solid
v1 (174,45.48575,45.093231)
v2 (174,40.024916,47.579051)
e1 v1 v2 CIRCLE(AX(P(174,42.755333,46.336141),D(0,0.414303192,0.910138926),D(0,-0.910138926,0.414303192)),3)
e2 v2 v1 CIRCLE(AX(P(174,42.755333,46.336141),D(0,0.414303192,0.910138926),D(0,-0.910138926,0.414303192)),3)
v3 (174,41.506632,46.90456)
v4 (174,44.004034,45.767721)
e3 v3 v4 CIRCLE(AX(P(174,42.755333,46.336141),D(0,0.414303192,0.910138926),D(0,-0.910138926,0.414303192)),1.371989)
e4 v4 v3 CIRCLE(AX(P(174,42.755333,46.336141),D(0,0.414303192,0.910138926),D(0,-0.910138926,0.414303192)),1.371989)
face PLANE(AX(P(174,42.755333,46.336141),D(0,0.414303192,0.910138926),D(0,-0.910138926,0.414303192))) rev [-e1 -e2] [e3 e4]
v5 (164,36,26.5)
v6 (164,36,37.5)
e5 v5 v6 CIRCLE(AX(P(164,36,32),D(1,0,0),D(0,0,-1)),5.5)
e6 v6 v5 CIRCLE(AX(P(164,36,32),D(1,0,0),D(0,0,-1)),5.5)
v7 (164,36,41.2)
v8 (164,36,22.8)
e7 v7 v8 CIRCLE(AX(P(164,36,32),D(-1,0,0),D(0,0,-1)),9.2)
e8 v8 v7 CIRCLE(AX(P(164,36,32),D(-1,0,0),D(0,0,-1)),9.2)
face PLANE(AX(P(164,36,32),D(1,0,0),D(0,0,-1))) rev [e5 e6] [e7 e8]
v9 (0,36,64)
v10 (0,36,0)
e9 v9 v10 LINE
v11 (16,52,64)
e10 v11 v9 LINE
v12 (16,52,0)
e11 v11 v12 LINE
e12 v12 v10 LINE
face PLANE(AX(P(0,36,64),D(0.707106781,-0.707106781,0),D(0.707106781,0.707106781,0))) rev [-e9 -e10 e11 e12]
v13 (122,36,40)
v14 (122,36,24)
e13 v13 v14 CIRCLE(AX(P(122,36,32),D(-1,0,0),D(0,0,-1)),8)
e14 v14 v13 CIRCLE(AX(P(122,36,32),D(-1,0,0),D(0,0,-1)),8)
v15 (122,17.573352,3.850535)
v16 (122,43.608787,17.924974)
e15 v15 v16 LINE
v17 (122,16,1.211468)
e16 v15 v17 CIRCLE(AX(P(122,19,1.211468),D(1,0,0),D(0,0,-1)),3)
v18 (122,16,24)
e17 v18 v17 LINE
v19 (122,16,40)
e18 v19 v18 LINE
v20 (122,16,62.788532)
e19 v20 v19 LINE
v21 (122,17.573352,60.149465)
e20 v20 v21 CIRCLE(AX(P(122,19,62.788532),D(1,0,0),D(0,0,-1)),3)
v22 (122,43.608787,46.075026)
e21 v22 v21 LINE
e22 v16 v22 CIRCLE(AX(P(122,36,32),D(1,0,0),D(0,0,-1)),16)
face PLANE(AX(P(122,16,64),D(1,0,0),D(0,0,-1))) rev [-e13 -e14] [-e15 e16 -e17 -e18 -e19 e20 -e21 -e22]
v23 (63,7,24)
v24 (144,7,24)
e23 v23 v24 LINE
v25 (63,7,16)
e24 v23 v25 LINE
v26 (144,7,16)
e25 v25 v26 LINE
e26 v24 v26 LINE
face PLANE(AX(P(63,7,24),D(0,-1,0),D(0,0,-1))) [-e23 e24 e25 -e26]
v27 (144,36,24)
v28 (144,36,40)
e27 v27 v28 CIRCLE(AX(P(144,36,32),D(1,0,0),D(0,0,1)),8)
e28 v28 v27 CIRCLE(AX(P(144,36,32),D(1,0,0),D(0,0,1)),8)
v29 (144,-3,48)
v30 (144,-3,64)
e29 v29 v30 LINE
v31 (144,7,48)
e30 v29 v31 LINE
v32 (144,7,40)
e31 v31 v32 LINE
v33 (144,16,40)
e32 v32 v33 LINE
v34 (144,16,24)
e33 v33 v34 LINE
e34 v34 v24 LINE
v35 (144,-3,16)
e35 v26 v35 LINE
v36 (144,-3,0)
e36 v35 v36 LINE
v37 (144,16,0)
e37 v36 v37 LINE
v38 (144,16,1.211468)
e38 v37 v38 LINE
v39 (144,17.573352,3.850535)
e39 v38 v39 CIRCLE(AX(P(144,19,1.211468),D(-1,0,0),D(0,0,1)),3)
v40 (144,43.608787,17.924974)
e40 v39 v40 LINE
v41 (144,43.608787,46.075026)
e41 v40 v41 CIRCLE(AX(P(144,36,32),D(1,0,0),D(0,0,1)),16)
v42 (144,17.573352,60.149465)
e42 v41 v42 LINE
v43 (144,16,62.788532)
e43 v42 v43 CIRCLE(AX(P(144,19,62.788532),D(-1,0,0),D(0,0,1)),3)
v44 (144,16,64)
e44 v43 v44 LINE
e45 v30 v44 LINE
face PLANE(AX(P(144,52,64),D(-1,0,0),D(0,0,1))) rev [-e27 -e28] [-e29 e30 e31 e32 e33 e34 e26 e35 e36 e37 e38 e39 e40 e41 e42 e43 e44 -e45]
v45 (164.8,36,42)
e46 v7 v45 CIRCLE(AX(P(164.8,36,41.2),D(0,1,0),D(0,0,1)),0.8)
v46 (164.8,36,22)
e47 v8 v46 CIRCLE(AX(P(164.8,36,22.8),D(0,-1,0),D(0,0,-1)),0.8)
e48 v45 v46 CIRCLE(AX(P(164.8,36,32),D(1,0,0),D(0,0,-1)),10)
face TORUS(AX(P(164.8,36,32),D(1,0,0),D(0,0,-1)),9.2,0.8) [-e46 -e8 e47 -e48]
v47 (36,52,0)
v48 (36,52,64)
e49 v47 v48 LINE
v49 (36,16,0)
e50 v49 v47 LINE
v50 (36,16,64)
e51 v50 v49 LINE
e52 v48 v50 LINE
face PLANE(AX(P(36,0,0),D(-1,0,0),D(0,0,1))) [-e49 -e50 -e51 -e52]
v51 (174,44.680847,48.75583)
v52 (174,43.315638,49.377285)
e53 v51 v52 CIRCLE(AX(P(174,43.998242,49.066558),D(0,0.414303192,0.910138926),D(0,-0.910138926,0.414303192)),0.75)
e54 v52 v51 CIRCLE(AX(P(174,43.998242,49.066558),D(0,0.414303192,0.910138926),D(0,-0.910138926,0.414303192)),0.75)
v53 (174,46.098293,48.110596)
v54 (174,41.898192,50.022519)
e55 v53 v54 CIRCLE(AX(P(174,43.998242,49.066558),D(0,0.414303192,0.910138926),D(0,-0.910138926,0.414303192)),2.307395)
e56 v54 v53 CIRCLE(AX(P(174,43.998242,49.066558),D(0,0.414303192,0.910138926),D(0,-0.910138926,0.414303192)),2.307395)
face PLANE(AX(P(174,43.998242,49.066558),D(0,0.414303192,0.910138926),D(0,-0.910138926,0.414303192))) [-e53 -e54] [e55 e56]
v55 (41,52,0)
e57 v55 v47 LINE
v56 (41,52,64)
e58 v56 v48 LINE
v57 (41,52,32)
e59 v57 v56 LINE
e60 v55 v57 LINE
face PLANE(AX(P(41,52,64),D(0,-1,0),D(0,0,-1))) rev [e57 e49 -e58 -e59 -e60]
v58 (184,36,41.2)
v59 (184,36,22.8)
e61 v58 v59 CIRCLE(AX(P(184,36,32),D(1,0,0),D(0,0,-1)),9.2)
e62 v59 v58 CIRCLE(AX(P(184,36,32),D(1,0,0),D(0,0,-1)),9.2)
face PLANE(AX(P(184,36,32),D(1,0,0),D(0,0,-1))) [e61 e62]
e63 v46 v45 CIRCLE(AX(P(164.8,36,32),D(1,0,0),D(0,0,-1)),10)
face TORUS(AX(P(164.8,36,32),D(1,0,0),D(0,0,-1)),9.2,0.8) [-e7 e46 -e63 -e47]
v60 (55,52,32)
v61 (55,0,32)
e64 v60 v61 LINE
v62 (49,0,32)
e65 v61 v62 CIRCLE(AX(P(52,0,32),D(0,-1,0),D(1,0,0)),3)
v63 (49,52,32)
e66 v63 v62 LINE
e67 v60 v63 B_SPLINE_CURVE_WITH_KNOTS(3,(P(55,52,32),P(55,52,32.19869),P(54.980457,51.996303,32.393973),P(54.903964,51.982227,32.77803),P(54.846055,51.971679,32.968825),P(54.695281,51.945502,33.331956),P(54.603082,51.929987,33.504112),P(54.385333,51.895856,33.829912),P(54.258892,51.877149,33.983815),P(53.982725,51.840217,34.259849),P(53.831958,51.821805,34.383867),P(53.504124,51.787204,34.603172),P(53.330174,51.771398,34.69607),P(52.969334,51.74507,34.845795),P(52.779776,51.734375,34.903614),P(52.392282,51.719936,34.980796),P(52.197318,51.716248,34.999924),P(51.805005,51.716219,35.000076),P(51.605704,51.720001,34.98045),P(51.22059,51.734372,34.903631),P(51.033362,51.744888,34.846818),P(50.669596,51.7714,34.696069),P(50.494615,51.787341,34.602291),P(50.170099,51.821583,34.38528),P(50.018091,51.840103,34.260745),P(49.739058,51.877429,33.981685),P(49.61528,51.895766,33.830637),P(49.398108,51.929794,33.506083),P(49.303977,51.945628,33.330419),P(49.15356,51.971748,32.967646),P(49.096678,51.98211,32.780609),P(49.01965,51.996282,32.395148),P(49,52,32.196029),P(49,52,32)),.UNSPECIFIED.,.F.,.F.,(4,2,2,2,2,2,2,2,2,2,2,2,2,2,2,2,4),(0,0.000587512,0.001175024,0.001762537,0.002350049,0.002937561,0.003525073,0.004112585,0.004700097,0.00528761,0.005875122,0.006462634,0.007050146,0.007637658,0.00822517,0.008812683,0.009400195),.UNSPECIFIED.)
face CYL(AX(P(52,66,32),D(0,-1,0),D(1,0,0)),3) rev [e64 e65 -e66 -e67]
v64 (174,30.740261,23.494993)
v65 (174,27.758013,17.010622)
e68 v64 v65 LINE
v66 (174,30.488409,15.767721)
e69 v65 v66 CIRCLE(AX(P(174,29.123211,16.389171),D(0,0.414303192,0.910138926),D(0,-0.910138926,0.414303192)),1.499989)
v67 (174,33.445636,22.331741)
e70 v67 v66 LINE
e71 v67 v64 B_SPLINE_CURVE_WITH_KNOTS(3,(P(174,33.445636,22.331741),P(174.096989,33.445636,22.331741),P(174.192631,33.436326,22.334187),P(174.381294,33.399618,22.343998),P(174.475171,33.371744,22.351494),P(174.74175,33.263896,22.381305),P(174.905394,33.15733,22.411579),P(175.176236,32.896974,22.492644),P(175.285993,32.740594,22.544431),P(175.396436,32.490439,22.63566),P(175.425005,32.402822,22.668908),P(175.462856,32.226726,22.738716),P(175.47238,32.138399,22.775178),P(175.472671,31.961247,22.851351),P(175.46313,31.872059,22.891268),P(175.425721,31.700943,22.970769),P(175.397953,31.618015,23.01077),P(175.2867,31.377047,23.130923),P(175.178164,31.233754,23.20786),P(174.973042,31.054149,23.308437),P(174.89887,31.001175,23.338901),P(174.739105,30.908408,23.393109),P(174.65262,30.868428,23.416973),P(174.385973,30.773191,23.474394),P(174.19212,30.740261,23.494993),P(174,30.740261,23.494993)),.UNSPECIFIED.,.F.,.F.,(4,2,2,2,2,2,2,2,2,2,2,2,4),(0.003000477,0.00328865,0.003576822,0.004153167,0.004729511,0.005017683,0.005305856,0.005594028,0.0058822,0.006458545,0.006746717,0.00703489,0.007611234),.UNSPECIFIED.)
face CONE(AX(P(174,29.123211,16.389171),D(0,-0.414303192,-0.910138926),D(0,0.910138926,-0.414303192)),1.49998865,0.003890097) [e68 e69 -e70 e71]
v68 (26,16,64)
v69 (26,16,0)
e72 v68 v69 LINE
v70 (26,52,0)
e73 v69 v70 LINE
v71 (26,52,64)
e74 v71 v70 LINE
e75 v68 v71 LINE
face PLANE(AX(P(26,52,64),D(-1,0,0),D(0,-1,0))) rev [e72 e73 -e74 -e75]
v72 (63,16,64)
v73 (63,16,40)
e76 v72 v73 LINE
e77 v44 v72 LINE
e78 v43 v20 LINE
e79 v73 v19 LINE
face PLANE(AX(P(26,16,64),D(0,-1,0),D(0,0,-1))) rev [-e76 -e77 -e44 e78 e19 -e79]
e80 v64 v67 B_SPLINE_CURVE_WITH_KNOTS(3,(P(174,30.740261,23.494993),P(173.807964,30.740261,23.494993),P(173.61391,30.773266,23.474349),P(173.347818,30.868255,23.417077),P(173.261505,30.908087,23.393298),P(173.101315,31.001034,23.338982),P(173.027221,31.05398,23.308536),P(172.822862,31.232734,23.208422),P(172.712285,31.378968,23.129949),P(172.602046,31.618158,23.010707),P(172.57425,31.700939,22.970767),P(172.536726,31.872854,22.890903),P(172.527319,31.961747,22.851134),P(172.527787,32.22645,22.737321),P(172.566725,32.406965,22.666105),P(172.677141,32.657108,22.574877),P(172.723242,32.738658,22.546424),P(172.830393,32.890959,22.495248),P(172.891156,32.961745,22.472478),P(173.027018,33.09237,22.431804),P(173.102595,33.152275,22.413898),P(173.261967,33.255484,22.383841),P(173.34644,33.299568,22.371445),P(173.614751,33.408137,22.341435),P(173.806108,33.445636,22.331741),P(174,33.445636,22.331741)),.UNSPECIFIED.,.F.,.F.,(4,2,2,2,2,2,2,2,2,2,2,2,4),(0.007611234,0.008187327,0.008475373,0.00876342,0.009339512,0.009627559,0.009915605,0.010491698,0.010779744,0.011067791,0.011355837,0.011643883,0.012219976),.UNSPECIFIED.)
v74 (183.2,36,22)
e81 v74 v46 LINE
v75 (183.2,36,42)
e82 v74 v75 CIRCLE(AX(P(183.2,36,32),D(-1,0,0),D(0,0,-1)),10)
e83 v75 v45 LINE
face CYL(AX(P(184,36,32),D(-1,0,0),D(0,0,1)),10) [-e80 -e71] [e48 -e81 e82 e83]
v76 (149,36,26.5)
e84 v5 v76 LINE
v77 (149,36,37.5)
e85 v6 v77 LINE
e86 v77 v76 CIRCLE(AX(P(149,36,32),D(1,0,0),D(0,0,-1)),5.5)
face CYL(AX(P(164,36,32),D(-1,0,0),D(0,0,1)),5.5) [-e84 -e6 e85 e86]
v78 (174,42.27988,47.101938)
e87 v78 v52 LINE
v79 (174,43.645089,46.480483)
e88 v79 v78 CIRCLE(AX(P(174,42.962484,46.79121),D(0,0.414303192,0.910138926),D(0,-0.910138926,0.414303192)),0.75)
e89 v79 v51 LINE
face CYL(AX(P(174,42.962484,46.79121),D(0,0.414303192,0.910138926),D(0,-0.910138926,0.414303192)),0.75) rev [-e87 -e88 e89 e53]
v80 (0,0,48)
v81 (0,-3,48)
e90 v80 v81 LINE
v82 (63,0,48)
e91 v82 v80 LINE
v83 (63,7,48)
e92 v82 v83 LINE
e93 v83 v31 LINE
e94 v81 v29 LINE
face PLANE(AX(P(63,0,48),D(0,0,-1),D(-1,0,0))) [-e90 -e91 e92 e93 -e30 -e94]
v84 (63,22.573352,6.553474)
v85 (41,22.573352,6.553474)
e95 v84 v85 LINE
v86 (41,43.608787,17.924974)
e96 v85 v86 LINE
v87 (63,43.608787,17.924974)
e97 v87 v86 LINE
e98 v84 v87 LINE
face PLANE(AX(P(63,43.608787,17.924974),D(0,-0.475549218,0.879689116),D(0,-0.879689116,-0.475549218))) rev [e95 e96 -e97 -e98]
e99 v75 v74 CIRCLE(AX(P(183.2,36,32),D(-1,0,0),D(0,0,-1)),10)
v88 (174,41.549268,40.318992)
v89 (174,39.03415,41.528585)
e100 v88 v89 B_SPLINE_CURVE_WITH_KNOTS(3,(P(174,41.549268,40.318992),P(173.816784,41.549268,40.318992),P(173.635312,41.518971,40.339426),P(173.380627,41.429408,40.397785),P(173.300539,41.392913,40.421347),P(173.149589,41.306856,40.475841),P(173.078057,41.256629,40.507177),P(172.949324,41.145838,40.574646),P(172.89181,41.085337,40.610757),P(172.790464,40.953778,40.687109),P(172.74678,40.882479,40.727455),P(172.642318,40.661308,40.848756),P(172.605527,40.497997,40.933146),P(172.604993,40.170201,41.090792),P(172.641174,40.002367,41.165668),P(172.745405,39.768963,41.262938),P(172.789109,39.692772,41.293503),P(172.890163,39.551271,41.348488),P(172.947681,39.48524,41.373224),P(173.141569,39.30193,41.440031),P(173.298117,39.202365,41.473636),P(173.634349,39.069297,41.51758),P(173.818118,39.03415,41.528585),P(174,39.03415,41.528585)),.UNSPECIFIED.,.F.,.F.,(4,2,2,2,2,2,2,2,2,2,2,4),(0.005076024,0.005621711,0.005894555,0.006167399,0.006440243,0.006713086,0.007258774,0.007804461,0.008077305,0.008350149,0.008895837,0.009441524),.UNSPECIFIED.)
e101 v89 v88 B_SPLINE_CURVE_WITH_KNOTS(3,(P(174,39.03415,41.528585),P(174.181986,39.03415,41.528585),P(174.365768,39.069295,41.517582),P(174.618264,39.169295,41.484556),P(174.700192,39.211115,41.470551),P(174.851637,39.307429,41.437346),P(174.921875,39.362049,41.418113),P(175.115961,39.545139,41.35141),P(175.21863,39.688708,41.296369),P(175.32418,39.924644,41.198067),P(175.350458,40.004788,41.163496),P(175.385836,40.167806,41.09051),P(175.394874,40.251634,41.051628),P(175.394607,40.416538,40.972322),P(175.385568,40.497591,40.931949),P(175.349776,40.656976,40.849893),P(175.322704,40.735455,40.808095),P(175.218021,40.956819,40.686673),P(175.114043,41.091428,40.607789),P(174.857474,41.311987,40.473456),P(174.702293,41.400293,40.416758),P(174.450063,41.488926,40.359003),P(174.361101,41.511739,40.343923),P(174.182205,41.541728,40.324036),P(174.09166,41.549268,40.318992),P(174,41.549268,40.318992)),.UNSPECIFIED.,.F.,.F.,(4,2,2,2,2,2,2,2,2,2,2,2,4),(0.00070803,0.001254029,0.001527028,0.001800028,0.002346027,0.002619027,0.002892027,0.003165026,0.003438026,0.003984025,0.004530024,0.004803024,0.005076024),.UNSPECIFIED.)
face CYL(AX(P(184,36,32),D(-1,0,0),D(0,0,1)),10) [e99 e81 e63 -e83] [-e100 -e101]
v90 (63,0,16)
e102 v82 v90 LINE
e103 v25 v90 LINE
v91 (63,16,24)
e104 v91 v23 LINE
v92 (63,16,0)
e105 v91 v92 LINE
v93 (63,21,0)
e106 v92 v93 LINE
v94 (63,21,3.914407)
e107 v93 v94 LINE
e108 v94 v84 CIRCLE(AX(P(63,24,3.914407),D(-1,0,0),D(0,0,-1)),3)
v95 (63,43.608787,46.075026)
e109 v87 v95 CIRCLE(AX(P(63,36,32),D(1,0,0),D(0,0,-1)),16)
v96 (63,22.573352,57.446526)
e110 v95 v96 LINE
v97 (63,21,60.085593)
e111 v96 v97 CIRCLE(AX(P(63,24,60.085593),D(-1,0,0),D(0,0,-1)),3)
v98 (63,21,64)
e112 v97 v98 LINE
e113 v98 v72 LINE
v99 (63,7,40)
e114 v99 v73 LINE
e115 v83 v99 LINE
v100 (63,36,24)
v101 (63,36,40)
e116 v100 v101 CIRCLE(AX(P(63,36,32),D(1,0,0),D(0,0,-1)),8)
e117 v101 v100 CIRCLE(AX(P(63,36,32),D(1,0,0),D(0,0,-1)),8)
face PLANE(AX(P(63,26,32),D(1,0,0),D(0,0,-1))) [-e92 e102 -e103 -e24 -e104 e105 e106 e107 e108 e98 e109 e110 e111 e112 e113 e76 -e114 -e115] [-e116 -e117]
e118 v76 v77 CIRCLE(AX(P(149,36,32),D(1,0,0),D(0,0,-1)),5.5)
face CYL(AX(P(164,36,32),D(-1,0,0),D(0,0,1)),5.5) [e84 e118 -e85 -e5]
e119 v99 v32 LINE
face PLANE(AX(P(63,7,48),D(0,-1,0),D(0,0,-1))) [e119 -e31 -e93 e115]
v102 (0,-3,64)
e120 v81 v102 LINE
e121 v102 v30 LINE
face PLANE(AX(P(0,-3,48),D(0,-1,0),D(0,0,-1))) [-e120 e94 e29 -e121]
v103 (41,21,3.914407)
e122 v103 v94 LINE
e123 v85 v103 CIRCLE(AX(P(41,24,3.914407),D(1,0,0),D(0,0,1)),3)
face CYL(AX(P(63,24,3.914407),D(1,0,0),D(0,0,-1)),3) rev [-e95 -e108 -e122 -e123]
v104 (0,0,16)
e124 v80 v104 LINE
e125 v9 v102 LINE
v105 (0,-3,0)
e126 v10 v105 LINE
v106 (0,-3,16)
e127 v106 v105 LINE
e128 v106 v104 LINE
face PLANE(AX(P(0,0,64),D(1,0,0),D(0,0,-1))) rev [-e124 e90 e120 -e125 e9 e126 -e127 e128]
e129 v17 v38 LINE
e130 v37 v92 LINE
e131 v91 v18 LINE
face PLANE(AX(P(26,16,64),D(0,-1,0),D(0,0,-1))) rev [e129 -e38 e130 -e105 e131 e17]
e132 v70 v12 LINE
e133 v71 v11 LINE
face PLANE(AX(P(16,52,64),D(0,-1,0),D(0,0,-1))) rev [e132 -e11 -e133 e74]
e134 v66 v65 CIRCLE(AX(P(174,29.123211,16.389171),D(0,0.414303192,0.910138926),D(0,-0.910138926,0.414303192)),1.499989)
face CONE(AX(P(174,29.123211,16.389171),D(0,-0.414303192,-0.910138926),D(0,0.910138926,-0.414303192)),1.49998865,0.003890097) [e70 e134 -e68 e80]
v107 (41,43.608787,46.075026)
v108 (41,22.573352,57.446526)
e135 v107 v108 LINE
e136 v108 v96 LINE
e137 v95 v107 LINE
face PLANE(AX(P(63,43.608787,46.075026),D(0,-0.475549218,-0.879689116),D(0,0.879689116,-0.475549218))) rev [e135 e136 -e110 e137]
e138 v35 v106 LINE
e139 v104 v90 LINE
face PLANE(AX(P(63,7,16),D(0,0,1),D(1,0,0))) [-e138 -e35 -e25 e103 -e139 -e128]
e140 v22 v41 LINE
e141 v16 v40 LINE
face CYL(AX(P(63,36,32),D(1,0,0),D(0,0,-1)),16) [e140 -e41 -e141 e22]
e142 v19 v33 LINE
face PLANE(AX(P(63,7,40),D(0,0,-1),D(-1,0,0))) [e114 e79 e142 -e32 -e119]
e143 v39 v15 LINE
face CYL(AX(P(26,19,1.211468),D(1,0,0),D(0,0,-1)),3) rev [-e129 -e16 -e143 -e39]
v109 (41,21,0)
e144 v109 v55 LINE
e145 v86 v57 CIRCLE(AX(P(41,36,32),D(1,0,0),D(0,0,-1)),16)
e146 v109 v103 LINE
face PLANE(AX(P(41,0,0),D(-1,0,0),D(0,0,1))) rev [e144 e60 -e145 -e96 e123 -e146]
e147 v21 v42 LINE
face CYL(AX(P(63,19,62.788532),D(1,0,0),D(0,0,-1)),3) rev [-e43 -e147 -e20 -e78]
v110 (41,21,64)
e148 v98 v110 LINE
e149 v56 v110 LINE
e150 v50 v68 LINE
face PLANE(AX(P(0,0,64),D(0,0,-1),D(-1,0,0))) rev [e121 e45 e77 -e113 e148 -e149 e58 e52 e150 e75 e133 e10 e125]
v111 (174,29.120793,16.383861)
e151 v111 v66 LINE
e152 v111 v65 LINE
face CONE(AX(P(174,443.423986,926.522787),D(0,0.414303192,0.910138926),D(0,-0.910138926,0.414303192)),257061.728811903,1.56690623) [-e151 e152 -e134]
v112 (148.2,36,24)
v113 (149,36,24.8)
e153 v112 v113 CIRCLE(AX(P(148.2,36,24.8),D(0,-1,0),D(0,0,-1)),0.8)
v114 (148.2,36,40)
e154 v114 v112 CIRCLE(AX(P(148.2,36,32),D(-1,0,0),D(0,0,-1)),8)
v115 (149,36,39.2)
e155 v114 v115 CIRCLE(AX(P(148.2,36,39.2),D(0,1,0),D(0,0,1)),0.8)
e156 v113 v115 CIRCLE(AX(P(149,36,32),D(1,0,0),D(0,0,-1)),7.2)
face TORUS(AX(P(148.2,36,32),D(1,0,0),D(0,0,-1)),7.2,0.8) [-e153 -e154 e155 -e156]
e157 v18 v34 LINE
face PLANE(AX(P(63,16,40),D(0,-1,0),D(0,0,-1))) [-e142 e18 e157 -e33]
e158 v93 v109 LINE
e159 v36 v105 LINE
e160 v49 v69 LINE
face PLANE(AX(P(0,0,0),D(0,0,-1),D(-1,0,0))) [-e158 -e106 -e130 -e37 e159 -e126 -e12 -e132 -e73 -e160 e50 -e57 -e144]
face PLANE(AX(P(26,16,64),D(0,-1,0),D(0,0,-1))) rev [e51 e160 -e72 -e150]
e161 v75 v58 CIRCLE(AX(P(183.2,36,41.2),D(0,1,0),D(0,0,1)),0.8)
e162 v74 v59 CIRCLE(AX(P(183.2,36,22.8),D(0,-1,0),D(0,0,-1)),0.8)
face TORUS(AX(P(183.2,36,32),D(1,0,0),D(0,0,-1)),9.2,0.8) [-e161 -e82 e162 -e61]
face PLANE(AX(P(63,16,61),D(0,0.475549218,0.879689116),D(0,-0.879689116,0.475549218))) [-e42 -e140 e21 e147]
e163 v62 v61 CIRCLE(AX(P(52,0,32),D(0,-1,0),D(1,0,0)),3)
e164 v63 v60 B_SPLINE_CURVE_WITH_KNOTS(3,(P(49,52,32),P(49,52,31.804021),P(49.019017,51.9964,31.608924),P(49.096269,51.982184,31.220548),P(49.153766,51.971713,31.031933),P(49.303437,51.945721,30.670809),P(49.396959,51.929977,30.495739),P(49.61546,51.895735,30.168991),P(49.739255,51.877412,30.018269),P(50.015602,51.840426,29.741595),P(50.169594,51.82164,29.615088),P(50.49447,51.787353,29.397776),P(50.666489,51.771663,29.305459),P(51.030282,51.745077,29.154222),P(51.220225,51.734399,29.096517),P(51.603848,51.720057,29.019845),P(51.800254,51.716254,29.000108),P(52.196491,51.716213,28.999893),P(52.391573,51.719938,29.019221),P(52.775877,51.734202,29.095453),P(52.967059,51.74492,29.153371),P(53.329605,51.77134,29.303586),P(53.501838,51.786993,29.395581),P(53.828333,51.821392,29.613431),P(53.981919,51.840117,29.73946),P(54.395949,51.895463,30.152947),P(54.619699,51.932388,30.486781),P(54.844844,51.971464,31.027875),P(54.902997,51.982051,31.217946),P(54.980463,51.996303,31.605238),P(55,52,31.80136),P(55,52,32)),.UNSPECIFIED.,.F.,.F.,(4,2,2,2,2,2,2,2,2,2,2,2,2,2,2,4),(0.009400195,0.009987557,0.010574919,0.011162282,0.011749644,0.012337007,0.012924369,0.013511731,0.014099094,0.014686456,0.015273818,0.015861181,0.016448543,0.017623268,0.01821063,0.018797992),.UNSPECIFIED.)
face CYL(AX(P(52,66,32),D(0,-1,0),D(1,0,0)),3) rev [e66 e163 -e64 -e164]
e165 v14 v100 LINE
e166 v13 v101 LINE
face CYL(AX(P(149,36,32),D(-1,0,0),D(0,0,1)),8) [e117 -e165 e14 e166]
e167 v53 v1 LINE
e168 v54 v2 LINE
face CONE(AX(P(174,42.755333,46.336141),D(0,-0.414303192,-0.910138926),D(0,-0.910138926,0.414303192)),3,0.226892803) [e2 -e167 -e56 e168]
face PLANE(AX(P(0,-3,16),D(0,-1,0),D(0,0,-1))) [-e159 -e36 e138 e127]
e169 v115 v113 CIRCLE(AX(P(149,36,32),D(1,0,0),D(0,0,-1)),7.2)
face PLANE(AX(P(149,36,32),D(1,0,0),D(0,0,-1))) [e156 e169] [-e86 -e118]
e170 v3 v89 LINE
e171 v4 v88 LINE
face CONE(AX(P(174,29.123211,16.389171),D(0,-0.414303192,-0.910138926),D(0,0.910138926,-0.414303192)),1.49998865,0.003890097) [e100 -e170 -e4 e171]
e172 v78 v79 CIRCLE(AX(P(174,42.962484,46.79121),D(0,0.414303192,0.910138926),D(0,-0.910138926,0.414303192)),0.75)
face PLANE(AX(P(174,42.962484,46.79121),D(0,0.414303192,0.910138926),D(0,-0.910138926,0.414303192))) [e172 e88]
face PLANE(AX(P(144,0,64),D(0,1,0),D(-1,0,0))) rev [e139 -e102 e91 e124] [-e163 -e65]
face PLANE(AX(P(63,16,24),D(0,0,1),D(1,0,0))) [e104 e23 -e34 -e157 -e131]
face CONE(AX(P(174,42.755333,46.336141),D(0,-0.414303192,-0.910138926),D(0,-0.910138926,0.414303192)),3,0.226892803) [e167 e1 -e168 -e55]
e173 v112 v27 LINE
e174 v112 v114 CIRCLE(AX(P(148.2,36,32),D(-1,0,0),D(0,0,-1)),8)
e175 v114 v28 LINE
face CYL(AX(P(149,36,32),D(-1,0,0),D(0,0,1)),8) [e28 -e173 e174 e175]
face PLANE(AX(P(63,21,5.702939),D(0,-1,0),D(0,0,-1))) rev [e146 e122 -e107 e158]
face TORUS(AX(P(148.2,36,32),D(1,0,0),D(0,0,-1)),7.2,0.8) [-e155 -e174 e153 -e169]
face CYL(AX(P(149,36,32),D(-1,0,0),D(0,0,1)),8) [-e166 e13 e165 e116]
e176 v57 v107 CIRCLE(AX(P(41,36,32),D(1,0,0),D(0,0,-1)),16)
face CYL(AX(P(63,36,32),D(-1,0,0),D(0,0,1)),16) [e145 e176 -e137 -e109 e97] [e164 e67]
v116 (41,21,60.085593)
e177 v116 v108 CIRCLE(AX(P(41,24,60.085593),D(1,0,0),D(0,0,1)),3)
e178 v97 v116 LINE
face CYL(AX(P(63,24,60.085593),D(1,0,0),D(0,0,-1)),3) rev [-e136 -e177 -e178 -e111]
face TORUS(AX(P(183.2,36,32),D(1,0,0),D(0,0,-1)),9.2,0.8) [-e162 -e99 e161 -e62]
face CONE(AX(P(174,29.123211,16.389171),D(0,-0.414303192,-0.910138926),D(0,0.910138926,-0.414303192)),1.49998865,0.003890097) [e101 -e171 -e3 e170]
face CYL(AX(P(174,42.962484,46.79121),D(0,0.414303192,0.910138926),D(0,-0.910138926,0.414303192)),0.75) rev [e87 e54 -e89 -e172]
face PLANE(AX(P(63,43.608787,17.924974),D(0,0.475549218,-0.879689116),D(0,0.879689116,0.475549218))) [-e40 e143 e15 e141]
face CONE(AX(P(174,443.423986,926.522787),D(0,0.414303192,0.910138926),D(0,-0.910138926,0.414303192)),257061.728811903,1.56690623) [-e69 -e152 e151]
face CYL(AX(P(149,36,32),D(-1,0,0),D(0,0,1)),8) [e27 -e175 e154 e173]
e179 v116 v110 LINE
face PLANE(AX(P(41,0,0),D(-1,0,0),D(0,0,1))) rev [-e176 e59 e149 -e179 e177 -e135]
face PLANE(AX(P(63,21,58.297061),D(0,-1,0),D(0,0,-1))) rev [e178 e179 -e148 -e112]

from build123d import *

# Parameters (mm, degrees)
VISE_BODY_DEPTH                 = 64
GUIDE_CHANNEL_PROFILE_OUTSIDE_W = 99.188
GUIDE_CHANNEL_PROFILE_OUTSIDE_H = 87.188
GUIDE_CHANNEL_CUT_DEPTH         = 81
SUPPORT_PLATE_PROFILE_W         = 64
SUPPORT_PLATE_PROFILE_H         = 52
SUPPORT_PLATE_DEPTH             = 5
JAW_START                       = 22
JAW_BLOCK_DEPTH                 = 22
LEAD_SCREW_SHAFT_16_DEPTH       = 5
LEAD_SCREW_SHAFT_16_DEPTH_BACK  = 81
LEAD_SCREW_PROFILE_16_R         = 8
SCREW_NECK_PROFILE_11_R         = 5.5
SCREW_NECK_11_DEPTH             = 15
HANDLE_HUB_PROFILE_20_R         = 10
HANDLE_HUB_20_DEPTH             = 20
JAW_BLOCK_FILLET_R3_R           = 3
JAW_BLOCK_CHANNEL_FILLET_R3_R   = 3
PIN_BOSS_PROFILE_6_R            = 3
PIN_BOSS_6_DEPTH                = 3
PIN_BOSS_6_TAPER                = 13
PIN_HOLE_PROFILE_1_5_R          = 0.75
PIN_HOLE_1_5_DEPTH              = 2.5
BASE_FOOT_PROFILE_W             = 144
BASE_FOOT_PROFILE_H             = 3
BASE_FOOT_DEPTH                 = 16
FOOT_EXTENSION_PROFILE_W        = 144
FOOT_EXTENSION_PROFILE_H        = 3
FOOT_EXTENSION_DEPTH            = 16
JAW_HOLE_PROFILE_6_R            = 3
JAW_HOLE_6_DEPTH                = 66
HANDLE_HUB_FILLET_R0_8_R        = 0.8
LEAD_SCREW_FILLET_R0_8_R        = 0.8


with BuildPart() as part:
    # Vise Body Profile → Vise Body (new body)
    with BuildSketch(Plane.XY):
        Polygon((0, 0), (0, 36), (16, 52), (26, 52), (26, 16), (122, 16), (122, 52), (144, 52), (144, 0), align=None)
    extrude(amount=VISE_BODY_DEPTH)

    # Guide Channel Profile outside → Guide Channel Cut (cut)
    with BuildSketch(Plane(origin=(144, 0, 0), x_dir=(0, 0, -1), z_dir=(1, 0, 0))):
        with Locations((-32, 26)):
            Rectangle(GUIDE_CHANNEL_PROFILE_OUTSIDE_W, GUIDE_CHANNEL_PROFILE_OUTSIDE_H)
        with BuildLine():
            Line((-64, 0), (-48, 0))
            Line((-48, 0), (-48, 7))
            Line((-48, 7), (-40, 7))
            Line((-40, 7), (-40, 16))
            Line((-40, 16), (-24, 16))
            Line((-24, 16), (-24, 7))
            Line((-24, 7), (-16, 7))
            Line((-16, 7), (-16, 0))
            Line((-16, 0), (0, 0))
            Line((0, 0), (0, 16))
            Line((0, 16), (-3, 16))
            Line((-3, 16), (-17.924974143, 43.608787493))
            ThreePointArc((-17.924974143, 43.608787493), (-32, 52), (-46.075025857, 43.608787493))
            Line((-46.075025857, 43.608787493), (-61, 16))
            Line((-61, 16), (-64, 16))
            Line((-64, 16), (-64, 0))
        make_face(mode=Mode.SUBTRACT)
    extrude(amount=-GUIDE_CHANNEL_CUT_DEPTH, mode=Mode.SUBTRACT)

    # Support Plate Profile → Support Plate (add)
    with BuildSketch(Plane(origin=(36, 0, 0), x_dir=(0, 0, -1), z_dir=(1, 0, 0))):
        with Locations((-32, 26)):
            Rectangle(SUPPORT_PLATE_PROFILE_W, SUPPORT_PLATE_PROFILE_H)
    extrude(amount=SUPPORT_PLATE_DEPTH)

    # Jaw Block Profile → Jaw Block (add)
    with BuildSketch(Plane(origin=(41, 0, 0), x_dir=(0, 0, -1), z_dir=(1, 0, 0)).offset(JAW_START)):
        with BuildLine():
            Line((-46.075025857, 43.608787493), (-58.297060918, 21))
            Line((-58.297060918, 21), (-64, 21))
            Line((-64, 21), (-64, 16))
            Line((-64, 16), (0, 16))
            Line((0, 16), (0, 21))
            Line((0, 21), (-5.702939082, 21))
            Line((-5.702939082, 21), (-17.924974143, 43.608787493))
            ThreePointArc((-17.924974143, 43.608787493), (-32, 52), (-46.075025857, 43.608787493))
        make_face()
    extrude(amount=-JAW_BLOCK_DEPTH)

    # Lead Screw Profile Ø16 → Lead Screw Shaft Ø16 (add, two sides: drawn at the far end of the back side and taken through both)
    with BuildSketch(Plane(origin=(144, 0, 0), x_dir=(0, 0, -1), z_dir=(1, 0, 0)).offset(-LEAD_SCREW_SHAFT_16_DEPTH_BACK)):
        with Locations((-32, 36)):
            Circle(LEAD_SCREW_PROFILE_16_R)
    extrude(amount=LEAD_SCREW_SHAFT_16_DEPTH + LEAD_SCREW_SHAFT_16_DEPTH_BACK)

    # Screw Neck Profile Ø11 → Screw Neck Ø11 (add)
    with BuildSketch(Plane(origin=(149, 0, 0), x_dir=(0, 0, -1), z_dir=(1, 0, 0))):
        with Locations((-32, 36)):
            Circle(SCREW_NECK_PROFILE_11_R)
    extrude(amount=SCREW_NECK_11_DEPTH)

    # Handle Hub Profile Ø20 → Handle Hub Ø20 (add)
    with BuildSketch(Plane(origin=(164, 0, 0), x_dir=(0, 0, -1), z_dir=(1, 0, 0))):
        with Locations((-32, 36)):
            Circle(HANDLE_HUB_PROFILE_20_R)
    extrude(amount=HANDLE_HUB_20_DEPTH)

    # Jaw Block Fillet R3
    jaw_block_fillet_r3_edges = [part.edges().sort_by_distance(p)[0] for p in [
        (52, 21, 58.297060918),
    ]]
    fillet(jaw_block_fillet_r3_edges, radius=JAW_BLOCK_FILLET_R3_R)

    # Jaw Block Channel Fillet R3
    jaw_block_channel_fillet_r3_edges = [part.edges().sort_by_distance(p)[0] for p in [
        (52, 21, 5.702939082),
        (133, 16, 3),
        (133, 16, 61),
    ]]
    fillet(jaw_block_channel_fillet_r3_edges, radius=JAW_BLOCK_CHANNEL_FILLET_R3_R)

    # Collar Revolve Profile → Collar Revolve (revolve)
    with BuildSketch(Plane(origin=(174, 0, 0), x_dir=(0, 0, -1), z_dir=(1, 0, 0)), mode=Mode.PRIVATE) as collar_revolve_sk:
        Polygon((-45.767721385, 44.00403367), (-15.767721385, 30.48840867), (-16.383860693, 29.120793097), (-46.336140932, 42.755332802), align=None)
    revolve(collar_revolve_sk.sketch.rotate(Axis((174, 47.778525514, 57.371062468), (0, -0.41430319244059016, -0.9101389260621344)), 209.202366006), axis=Axis((174, 47.778525514, 57.371062468), (0, -0.41430319244059016, -0.9101389260621344)))

    # Pin Boss Profile Ø6 → Pin Boss Ø6 (add)
    with BuildSketch(Plane(origin=(0, 24.810959499, 54.504576467), x_dir=(1, 0, 0), z_dir=(0, 0.41430319244059144, 0.9101389260621338))):
        with Locations((174, 19.716081566)):
            Circle(PIN_BOSS_PROFILE_6_R)
    extrude(amount=PIN_BOSS_6_DEPTH, taper=PIN_BOSS_6_TAPER)

    # Pin Hole Profile Ø1.5 → Pin Hole Ø1.5 (cut)
    with BuildSketch(Plane(origin=(0, 26.053869076, 57.234993245), x_dir=(1, 0, 0), z_dir=(0, 0.41430319244059144, 0.9101389260621339))):
        with Locations(Location((174, 19.716081566, 0), (0, 0, 270))):
            Circle(PIN_HOLE_PROFILE_1_5_R)
    extrude(amount=-PIN_HOLE_1_5_DEPTH, mode=Mode.SUBTRACT)

    # Base Foot Profile → Base Foot (add)
    with BuildSketch(Plane.XY.offset(64)):
        with Locations((72, -1.5)):
            Rectangle(BASE_FOOT_PROFILE_W, BASE_FOOT_PROFILE_H)
    extrude(amount=-BASE_FOOT_DEPTH)

    # Foot Extension Profile → Foot Extension (add)
    with BuildSketch(Plane(origin=(0, 0, 0), x_dir=(-1, 0, 0), z_dir=(0, 0, -1))):
        with Locations((-72, -1.5)):
            Rectangle(FOOT_EXTENSION_PROFILE_W, FOOT_EXTENSION_PROFILE_H)
    extrude(amount=-FOOT_EXTENSION_DEPTH)

    # Jaw Hole Profile Ø6 → Jaw Hole Ø6 (cut)
    with BuildSketch(Plane.XZ):
        with Locations((52, 32)):
            Circle(JAW_HOLE_PROFILE_6_R)
    extrude(amount=-JAW_HOLE_6_DEPTH, mode=Mode.SUBTRACT)

    # Handle Hub Fillet R0.8
    handle_hub_fillet_r0_8_edges = [part.edges().sort_by_distance(p)[0] for p in [
        (164, 36, 42),
        (184, 36, 42),
    ]]
    fillet(handle_hub_fillet_r0_8_edges, radius=HANDLE_HUB_FILLET_R0_8_R)

    # Lead Screw Fillet R0.8
    lead_screw_fillet_r0_8_edges = [part.edges().sort_by_distance(p)[0] for p in [
        (149, 36, 40),
    ]]
    fillet(lead_screw_fillet_r0_8_edges, radius=LEAD_SCREW_FILLET_R0_8_R)


solid = part.part
